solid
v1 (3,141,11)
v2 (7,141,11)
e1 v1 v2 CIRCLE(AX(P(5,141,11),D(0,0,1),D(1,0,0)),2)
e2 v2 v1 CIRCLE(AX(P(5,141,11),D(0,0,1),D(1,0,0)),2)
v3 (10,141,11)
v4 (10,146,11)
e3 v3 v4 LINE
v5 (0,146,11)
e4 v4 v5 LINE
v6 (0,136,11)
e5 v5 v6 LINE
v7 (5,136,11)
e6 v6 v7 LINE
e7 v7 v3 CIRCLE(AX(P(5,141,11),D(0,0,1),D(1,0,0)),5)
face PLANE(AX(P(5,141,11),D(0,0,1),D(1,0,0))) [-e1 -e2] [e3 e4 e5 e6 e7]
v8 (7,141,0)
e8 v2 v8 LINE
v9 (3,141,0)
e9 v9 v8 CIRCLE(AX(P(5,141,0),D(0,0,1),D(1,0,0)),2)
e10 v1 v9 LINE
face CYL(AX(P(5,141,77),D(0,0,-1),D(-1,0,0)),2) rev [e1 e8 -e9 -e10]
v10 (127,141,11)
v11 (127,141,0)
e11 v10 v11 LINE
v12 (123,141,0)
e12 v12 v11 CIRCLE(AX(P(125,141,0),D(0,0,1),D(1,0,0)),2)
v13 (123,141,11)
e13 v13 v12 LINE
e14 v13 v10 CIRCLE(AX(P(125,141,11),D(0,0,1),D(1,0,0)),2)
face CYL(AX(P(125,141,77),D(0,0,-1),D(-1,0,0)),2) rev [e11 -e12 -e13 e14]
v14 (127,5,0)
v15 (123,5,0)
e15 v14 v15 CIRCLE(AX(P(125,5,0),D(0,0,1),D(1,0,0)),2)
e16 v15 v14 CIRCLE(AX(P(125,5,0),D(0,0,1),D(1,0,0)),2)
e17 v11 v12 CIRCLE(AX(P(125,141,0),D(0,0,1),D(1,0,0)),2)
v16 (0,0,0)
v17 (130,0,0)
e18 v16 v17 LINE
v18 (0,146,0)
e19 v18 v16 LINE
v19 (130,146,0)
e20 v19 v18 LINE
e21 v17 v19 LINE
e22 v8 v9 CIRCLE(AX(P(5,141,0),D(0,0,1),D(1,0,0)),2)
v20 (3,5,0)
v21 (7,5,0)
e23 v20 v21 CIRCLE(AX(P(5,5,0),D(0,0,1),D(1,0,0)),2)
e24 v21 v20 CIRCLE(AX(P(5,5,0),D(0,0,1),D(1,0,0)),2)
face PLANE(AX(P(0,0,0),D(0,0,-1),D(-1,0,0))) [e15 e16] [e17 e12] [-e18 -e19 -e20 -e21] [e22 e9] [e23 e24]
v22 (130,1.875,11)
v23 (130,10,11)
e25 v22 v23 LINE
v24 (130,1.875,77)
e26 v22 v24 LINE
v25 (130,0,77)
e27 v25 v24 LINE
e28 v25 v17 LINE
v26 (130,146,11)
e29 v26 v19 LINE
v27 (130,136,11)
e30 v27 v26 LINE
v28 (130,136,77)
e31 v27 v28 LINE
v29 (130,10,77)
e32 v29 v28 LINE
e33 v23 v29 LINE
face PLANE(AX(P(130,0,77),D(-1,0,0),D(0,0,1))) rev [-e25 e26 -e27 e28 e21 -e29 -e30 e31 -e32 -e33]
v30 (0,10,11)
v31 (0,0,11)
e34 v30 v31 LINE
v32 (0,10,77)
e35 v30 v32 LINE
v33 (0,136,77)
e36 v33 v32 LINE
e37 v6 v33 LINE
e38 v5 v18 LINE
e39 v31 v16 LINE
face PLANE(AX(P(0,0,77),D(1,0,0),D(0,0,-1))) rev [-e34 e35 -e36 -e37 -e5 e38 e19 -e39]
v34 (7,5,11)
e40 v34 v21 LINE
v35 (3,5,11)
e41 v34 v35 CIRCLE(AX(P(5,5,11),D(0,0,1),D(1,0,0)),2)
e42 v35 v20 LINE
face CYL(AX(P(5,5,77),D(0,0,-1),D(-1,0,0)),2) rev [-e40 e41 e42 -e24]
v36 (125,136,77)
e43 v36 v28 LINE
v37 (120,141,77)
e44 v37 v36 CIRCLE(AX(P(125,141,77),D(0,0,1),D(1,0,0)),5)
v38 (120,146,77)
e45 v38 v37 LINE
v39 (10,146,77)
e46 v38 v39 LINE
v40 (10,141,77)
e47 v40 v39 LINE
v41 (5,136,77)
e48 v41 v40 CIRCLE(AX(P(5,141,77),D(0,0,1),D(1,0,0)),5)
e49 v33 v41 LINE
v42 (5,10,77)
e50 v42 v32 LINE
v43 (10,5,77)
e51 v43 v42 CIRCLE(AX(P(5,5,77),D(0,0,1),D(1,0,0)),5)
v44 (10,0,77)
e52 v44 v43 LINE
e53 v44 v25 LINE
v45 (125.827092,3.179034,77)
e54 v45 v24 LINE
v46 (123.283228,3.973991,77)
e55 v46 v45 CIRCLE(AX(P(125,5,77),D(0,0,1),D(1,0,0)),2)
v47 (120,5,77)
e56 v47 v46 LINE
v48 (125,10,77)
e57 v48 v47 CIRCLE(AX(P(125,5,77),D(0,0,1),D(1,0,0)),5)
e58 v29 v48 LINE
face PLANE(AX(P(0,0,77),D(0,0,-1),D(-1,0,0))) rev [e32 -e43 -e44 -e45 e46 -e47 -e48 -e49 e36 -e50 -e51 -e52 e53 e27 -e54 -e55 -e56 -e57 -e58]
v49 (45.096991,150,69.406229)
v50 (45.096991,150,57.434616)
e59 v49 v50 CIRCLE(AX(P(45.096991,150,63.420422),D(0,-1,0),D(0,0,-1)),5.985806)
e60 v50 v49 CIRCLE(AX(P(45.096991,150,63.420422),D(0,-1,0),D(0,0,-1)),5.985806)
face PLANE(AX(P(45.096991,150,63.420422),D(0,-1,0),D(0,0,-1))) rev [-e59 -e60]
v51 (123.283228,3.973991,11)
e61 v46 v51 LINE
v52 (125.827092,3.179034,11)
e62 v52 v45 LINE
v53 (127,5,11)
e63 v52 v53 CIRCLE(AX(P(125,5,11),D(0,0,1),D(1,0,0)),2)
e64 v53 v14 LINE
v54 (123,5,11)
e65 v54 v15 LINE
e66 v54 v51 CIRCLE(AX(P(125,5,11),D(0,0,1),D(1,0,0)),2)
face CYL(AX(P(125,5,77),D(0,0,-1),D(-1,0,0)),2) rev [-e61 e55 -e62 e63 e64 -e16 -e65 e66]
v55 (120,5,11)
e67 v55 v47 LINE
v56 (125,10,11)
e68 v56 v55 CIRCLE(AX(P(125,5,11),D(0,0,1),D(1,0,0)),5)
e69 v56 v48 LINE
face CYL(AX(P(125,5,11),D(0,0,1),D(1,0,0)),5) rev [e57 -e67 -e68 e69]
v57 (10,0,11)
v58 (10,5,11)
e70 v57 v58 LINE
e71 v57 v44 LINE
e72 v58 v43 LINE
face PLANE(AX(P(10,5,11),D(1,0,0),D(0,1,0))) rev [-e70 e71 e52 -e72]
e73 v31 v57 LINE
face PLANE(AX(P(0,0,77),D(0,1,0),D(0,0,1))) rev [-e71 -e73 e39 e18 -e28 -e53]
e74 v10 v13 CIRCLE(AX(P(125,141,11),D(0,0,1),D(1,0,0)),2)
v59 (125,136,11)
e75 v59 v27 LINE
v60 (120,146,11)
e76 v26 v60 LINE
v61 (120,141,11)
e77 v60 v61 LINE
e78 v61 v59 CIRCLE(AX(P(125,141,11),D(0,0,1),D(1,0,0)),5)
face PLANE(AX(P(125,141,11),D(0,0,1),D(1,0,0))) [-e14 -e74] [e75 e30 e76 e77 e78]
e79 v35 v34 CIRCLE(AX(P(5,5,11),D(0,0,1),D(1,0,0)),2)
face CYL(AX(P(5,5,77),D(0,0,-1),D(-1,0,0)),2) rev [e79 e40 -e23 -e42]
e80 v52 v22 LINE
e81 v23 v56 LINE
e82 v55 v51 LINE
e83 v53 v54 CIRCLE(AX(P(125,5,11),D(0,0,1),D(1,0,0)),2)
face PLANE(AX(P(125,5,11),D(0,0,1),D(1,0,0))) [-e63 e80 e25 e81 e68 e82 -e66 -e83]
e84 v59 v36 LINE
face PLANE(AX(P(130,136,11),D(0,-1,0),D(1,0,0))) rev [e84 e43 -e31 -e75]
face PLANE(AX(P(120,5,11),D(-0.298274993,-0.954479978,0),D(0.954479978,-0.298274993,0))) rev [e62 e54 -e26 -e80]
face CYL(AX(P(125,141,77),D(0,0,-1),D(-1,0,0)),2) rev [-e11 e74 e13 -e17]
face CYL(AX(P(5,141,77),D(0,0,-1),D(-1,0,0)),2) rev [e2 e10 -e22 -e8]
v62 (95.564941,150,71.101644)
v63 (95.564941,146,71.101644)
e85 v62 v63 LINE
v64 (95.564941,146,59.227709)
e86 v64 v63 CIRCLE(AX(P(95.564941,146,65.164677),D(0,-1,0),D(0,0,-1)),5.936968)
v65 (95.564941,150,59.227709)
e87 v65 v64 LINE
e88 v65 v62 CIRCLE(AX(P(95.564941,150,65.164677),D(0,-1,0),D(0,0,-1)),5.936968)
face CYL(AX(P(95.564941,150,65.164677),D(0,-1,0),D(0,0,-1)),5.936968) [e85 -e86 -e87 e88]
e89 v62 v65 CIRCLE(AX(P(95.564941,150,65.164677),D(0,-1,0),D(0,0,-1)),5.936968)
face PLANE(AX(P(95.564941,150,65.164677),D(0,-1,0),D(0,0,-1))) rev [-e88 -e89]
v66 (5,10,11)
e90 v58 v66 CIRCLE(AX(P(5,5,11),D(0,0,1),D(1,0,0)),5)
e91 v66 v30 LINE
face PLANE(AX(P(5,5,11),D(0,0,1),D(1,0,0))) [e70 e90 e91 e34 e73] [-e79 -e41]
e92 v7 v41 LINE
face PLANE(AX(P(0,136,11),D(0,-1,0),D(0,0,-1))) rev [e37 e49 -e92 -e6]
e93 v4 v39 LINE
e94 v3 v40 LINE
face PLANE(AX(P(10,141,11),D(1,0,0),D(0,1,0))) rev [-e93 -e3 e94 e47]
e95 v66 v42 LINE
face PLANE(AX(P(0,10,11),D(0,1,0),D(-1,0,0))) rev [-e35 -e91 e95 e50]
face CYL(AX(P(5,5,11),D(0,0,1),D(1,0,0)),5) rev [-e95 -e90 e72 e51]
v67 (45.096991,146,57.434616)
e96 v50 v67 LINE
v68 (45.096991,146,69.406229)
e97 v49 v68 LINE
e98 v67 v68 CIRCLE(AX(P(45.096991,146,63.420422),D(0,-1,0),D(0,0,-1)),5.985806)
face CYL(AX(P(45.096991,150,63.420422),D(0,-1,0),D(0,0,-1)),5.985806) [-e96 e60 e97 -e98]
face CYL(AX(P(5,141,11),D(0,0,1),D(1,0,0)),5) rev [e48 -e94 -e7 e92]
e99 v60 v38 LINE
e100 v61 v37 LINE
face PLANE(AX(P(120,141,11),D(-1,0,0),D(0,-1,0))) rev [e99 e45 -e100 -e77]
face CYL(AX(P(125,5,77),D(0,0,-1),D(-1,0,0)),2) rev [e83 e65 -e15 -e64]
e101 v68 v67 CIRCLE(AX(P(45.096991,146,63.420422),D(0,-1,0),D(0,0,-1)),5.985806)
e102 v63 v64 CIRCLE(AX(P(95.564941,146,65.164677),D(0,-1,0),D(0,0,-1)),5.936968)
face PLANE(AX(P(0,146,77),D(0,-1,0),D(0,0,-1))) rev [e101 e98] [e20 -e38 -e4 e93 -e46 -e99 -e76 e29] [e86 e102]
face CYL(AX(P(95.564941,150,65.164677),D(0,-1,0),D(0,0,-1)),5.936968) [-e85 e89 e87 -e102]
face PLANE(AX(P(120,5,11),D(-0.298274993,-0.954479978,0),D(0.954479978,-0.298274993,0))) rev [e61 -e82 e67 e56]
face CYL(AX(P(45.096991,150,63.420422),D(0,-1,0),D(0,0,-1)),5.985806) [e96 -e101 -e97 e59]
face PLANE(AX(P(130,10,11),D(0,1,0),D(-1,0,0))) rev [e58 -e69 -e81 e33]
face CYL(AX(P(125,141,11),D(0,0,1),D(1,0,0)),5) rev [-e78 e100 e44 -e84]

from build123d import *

# Parameters (mm, degrees)
SKETCH1_W           = 130
SKETCH1_H           = 146
SKETCH1_R           = 2
BOSS_EXTRUDE1_DEPTH = 77
CUT_EXTRUDE2_DEPTH  = 66
SKETCH4_R           = 5.985806468
SKETCH4_R_2         = 5.936967647
BOSS_EXTRUDE3_DEPTH = 150


with BuildPart() as part:
    # Sketch1 → Boss-Extrude1 (new body)
    with BuildSketch(Plane.XY):
        with Locations((65, 73)):
            Rectangle(SKETCH1_W, SKETCH1_H)
        with Locations((5, 141)):
            Circle(SKETCH1_R, mode=Mode.SUBTRACT)
        with Locations((125, 141)):
            Circle(SKETCH1_R, mode=Mode.SUBTRACT)
        with Locations((125, 5)):
            Circle(SKETCH1_R, mode=Mode.SUBTRACT)
        with Locations((5, 5)):
            Circle(SKETCH1_R, mode=Mode.SUBTRACT)
    extrude(amount=BOSS_EXTRUDE1_DEPTH)

    # Sketch3 → Cut-Extrude2 (cut)
    with BuildSketch(Plane.XY.offset(77)):
        with BuildLine():
            Line((120, 141), (120, 146))
            Line((120, 146), (146, 160))
            Line((146, 160), (130, 136))
            Line((130, 136), (125, 136))
            ThreePointArc((125, 136), (121.464466094, 137.464466094), (120, 141))
        make_face()
        with BuildLine():
            Line((10, 141), (10, 146))
            Line((10, 146), (0, 160))
            Line((0, 160), (0, 136))
            Line((0, 136), (5, 136))
            ThreePointArc((5, 136), (8.535533906, 137.464466094), (10, 141))
        make_face()
        with BuildLine():
            Line((10, 5), (10, 0))
            Line((10, 0), (0, 0))
            Line((0, 0), (0, 10))
            Line((0, 10), (5, 10))
            ThreePointArc((5, 10), (8.535533906, 8.535533906), (10, 5))
        make_face()
        with BuildLine():
            Line((120, 5), (136, 0))
            Line((136, 0), (146, 0))
            Line((146, 0), (130, 10))
            Line((130, 10), (125, 10))
            ThreePointArc((125, 10), (121.464466094, 8.535533906), (120, 5))
        make_face()
    extrude(amount=-CUT_EXTRUDE2_DEPTH, mode=Mode.SUBTRACT)

    # Sketch4 → Boss-Extrude3 (add)
    with BuildSketch(Plane(origin=(0, 0, 0), x_dir=(-1, 0, 0), z_dir=(0, -1, 0))):
        with Locations(Location((-45.096991408, -63.420422251, 0), (0, 0, 90))):
            Circle(SKETCH4_R)
        with Locations(Location((-95.564941336, -65.16467674, 0), (0, 0, 90))):
            Circle(SKETCH4_R_2)
    extrude(amount=-BOSS_EXTRUDE3_DEPTH)


solid = part.part
